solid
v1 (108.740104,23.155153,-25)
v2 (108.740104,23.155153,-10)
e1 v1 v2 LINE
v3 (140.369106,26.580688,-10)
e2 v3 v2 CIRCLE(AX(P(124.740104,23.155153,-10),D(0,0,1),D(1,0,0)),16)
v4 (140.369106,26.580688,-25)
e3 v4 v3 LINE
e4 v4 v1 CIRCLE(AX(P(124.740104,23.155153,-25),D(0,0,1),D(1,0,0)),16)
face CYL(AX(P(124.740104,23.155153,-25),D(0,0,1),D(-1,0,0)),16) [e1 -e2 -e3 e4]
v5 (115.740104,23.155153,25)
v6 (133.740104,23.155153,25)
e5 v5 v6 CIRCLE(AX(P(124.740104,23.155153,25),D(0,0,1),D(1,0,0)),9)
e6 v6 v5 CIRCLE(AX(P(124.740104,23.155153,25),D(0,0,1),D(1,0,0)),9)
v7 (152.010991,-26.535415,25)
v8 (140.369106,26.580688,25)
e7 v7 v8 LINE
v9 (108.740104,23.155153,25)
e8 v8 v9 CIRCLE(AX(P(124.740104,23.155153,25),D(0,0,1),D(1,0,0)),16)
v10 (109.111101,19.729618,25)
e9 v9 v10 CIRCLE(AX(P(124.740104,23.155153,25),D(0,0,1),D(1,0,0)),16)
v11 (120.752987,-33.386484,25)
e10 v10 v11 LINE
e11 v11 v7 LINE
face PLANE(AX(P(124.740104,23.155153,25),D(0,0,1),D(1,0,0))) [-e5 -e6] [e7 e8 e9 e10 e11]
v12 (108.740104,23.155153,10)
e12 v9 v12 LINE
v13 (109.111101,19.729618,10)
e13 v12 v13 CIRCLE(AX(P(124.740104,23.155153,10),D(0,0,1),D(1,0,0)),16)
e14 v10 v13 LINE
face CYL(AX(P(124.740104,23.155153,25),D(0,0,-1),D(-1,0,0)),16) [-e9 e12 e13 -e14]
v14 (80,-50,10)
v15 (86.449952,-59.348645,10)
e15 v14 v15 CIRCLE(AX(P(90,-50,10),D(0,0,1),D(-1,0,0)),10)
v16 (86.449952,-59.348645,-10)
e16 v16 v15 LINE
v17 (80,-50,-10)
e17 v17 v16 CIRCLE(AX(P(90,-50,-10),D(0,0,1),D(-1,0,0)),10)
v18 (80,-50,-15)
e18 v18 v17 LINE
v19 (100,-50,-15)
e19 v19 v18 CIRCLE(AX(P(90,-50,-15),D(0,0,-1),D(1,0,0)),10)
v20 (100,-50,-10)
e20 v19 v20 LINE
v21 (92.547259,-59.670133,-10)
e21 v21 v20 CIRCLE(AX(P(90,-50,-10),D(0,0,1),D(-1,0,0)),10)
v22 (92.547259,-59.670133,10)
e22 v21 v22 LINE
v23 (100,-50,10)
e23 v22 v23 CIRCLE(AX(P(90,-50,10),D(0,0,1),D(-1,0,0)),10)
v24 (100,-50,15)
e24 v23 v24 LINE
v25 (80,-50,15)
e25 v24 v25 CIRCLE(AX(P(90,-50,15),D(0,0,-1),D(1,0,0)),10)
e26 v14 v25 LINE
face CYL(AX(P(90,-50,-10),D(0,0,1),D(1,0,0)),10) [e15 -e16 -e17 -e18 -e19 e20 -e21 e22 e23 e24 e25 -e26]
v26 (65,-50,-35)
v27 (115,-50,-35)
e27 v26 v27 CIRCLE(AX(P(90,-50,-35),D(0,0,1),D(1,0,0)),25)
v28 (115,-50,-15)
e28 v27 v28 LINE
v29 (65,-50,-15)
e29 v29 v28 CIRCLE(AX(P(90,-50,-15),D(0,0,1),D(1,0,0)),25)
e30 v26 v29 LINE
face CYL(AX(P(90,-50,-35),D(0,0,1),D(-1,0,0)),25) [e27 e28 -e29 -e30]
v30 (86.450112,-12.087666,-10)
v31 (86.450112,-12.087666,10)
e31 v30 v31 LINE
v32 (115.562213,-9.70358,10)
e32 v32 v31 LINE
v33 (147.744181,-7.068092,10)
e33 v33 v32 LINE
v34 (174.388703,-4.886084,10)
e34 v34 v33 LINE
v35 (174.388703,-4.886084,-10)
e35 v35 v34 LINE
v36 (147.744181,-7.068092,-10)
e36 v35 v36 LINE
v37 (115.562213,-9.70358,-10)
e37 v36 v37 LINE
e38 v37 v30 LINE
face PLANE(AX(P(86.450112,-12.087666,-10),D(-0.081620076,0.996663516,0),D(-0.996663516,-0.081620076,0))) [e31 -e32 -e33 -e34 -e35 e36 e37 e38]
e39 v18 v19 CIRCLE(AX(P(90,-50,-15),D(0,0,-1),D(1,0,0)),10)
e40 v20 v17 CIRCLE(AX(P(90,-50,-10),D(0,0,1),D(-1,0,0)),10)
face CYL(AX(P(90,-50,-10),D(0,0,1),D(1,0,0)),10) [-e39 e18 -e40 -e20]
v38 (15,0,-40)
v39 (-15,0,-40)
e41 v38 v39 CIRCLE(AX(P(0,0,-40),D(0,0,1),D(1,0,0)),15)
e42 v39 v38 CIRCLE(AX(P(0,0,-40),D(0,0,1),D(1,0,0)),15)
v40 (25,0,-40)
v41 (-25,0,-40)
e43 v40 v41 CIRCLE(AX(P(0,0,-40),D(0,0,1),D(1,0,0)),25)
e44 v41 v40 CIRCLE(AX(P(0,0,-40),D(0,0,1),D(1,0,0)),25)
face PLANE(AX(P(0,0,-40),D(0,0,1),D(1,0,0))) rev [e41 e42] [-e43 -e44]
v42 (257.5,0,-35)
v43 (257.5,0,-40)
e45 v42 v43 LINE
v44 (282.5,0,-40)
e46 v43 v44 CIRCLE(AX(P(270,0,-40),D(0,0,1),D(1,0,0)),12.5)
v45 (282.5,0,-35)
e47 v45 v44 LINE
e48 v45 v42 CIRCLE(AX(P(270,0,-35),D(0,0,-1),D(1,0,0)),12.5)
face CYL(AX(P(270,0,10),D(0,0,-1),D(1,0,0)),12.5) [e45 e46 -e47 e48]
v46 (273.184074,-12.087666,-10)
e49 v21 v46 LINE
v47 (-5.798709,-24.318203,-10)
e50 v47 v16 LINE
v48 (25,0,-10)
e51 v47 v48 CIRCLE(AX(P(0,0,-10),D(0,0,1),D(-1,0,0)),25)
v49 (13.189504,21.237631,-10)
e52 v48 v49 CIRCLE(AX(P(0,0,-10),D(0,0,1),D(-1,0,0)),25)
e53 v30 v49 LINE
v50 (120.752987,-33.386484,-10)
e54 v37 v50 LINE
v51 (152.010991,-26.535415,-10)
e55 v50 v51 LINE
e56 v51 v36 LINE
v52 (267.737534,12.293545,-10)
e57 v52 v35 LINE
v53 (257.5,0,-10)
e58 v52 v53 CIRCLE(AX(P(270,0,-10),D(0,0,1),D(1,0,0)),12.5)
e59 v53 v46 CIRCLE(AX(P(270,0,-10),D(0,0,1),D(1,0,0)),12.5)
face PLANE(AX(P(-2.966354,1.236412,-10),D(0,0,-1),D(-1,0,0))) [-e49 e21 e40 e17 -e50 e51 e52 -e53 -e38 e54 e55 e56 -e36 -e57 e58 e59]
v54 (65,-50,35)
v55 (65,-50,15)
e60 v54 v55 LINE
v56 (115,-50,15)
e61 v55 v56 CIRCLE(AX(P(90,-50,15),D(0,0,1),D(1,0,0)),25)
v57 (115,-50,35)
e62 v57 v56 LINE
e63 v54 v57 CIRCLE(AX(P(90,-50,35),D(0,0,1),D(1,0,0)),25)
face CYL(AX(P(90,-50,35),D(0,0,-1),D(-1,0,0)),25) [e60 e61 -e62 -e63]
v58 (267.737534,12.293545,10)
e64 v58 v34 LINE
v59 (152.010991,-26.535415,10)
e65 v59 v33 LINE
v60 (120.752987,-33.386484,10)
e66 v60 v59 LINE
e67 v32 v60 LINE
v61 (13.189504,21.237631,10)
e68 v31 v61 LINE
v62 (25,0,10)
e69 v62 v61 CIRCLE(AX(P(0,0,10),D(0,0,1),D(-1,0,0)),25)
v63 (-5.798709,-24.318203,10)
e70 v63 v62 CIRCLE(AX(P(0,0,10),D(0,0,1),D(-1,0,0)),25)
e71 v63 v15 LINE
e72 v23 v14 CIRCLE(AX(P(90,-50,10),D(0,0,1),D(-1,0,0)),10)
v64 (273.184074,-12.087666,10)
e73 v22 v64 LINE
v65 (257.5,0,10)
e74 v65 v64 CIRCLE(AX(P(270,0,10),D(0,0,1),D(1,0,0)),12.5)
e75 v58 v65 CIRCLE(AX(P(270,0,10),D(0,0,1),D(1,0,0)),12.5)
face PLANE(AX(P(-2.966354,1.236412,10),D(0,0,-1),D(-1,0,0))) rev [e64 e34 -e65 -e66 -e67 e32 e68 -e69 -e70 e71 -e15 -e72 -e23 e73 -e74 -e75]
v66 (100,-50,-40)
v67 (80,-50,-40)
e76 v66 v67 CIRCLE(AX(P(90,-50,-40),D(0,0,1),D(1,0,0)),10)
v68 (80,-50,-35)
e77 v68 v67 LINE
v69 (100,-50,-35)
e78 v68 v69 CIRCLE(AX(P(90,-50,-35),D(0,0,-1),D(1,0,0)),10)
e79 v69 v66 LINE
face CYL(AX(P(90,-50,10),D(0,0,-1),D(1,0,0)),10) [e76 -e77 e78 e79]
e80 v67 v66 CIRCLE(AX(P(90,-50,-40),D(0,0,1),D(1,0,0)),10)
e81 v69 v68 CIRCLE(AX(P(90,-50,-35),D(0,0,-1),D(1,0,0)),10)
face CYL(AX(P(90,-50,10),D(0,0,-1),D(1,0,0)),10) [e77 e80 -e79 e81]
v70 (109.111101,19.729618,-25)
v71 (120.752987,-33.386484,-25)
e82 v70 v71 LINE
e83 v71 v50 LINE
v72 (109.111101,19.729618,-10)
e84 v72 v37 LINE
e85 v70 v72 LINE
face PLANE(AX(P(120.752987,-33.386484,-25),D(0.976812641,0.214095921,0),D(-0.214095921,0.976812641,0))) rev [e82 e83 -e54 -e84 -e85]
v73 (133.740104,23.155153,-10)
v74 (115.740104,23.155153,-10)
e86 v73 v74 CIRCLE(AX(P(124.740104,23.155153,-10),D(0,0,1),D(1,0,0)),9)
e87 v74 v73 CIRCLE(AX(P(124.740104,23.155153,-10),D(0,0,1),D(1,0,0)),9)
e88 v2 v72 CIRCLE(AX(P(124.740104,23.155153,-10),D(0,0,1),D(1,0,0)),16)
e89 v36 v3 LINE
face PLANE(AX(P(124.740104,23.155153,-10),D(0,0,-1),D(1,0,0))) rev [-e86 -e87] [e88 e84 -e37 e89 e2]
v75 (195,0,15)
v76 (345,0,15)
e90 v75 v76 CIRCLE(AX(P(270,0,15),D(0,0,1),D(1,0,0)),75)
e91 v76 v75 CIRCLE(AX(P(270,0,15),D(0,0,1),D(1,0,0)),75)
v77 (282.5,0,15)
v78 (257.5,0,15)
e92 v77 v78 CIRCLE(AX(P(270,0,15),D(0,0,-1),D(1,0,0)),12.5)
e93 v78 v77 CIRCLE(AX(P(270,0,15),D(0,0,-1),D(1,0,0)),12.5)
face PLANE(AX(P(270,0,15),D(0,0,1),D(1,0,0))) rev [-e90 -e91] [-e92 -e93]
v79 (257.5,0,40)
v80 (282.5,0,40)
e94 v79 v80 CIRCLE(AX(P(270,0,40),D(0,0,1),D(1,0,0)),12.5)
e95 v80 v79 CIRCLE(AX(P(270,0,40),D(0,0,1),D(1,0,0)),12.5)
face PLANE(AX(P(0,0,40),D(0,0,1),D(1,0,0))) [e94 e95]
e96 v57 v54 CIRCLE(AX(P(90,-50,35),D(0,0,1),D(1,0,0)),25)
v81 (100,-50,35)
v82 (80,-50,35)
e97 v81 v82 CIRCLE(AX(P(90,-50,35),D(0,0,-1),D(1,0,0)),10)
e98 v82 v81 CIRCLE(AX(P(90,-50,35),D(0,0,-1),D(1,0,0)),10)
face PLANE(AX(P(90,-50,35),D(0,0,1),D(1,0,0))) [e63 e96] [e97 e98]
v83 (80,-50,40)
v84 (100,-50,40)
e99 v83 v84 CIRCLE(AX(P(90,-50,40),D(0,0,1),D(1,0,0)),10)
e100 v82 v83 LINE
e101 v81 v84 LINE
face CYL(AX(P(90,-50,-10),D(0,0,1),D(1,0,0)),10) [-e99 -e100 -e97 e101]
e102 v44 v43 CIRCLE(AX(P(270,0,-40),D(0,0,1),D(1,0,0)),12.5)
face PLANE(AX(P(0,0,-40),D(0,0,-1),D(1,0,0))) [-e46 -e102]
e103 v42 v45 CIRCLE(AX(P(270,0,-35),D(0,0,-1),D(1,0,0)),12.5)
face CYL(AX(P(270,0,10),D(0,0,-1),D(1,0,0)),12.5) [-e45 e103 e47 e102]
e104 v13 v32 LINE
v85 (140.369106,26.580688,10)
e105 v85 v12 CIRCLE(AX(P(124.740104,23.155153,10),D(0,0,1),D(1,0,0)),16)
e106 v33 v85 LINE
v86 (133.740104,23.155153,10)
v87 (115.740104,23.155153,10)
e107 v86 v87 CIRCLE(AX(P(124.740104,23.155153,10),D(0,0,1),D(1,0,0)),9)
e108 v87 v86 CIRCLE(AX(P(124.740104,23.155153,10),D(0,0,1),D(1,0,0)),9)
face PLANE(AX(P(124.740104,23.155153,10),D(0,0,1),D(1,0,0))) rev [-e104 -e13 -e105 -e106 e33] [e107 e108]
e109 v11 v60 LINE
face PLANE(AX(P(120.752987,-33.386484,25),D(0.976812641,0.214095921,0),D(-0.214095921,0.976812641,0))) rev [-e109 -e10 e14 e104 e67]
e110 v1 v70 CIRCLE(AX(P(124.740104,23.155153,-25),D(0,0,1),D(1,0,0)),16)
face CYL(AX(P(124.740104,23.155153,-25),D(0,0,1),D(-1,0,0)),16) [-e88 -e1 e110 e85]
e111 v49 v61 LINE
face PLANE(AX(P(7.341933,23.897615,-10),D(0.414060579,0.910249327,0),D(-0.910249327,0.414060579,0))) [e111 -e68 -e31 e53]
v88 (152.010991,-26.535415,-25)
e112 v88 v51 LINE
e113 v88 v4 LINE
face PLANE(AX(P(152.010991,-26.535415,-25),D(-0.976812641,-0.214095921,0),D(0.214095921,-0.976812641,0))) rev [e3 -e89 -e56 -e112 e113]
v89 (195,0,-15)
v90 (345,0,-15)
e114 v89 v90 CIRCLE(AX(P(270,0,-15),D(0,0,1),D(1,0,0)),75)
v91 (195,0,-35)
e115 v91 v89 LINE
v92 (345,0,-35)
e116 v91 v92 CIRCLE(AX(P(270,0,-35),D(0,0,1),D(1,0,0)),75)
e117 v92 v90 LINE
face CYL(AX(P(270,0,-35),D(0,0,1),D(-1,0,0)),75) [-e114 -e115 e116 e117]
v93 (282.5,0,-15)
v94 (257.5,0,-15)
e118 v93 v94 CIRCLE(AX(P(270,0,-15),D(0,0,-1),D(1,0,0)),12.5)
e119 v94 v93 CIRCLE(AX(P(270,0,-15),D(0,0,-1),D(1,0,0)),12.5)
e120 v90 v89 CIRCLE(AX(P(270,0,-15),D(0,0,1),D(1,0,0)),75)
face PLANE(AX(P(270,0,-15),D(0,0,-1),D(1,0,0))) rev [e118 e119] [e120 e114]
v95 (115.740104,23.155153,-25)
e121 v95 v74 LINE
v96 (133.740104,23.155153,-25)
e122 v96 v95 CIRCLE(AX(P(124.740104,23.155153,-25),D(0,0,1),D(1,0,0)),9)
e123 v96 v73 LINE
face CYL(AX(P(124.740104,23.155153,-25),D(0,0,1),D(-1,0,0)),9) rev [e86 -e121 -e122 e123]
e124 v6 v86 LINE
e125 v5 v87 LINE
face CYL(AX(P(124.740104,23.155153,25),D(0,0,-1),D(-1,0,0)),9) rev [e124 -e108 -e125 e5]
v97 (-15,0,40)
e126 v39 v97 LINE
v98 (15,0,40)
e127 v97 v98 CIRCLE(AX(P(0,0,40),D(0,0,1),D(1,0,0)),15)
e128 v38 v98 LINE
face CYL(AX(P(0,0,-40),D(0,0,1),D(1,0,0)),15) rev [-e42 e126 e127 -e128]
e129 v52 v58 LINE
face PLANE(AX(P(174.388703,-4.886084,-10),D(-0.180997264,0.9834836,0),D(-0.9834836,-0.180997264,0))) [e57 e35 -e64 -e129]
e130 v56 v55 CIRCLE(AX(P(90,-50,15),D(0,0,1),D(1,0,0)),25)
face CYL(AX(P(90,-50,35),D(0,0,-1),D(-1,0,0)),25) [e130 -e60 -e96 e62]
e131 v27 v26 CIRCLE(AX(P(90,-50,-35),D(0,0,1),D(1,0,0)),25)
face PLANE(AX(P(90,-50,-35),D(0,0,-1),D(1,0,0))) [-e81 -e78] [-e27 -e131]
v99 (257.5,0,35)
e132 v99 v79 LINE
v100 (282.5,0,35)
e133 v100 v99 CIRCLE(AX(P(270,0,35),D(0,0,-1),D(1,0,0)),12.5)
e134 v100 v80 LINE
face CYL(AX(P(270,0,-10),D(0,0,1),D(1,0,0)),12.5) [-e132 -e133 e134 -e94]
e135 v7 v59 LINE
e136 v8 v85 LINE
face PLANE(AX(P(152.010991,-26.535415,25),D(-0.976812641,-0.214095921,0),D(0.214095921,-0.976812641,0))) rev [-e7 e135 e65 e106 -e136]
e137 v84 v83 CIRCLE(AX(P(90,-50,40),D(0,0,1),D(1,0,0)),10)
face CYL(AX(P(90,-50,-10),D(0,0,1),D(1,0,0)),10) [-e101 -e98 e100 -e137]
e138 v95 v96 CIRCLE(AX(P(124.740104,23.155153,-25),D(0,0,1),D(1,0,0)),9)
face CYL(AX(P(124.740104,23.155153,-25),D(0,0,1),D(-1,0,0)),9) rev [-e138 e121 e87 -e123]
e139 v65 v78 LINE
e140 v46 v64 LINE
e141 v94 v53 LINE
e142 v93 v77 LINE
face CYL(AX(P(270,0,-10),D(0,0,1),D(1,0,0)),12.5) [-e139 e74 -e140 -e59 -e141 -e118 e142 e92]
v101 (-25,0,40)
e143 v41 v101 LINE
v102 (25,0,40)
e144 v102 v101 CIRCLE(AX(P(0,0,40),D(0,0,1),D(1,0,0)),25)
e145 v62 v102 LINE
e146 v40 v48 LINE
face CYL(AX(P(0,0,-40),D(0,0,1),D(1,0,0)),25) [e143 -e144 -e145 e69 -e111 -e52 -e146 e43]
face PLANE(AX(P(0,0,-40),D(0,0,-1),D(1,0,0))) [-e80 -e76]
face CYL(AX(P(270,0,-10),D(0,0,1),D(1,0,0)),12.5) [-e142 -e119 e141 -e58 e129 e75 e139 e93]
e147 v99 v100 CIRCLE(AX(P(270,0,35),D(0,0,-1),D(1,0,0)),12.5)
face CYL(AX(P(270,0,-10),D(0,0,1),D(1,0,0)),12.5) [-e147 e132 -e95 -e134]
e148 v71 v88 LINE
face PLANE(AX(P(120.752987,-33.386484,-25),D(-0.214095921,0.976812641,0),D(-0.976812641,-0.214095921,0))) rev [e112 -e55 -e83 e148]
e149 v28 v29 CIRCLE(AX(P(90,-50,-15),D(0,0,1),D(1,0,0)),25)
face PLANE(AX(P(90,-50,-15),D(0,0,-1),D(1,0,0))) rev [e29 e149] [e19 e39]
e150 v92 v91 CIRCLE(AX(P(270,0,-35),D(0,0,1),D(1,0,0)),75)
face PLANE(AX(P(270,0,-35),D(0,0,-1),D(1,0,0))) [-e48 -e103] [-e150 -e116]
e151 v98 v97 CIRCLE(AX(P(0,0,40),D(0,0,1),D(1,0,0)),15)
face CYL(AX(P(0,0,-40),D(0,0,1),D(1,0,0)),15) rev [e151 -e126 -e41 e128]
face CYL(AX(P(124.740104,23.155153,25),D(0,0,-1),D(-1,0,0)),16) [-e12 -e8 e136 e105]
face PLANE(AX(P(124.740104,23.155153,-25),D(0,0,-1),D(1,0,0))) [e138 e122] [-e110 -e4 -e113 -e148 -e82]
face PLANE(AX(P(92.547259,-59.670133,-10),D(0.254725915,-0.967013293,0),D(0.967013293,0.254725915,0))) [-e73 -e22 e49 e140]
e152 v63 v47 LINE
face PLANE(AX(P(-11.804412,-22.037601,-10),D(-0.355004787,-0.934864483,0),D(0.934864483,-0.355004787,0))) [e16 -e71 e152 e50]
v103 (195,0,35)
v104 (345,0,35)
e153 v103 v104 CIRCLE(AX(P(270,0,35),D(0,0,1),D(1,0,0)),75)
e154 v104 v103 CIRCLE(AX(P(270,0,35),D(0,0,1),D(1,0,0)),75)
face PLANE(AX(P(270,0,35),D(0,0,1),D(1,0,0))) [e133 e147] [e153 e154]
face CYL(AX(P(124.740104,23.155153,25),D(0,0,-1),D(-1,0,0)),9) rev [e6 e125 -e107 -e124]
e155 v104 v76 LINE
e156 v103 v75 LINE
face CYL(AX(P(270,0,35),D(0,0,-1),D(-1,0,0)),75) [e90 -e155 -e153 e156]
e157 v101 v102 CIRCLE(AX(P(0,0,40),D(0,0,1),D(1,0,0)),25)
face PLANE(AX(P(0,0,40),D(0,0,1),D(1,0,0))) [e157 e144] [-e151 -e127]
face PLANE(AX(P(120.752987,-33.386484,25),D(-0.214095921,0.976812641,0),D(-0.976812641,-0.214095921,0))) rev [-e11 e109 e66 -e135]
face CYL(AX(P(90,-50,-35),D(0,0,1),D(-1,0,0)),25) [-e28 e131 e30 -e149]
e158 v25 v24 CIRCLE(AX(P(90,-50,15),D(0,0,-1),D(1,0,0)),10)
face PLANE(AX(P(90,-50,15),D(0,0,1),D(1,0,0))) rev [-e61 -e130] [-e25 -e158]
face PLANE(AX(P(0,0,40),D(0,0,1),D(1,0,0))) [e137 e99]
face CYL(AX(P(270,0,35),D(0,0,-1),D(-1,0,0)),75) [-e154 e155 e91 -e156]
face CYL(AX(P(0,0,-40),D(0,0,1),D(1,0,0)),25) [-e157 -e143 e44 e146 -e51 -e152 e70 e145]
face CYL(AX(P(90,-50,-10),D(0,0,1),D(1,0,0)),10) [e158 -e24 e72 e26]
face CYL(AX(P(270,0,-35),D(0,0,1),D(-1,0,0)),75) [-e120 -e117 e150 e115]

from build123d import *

# Parameters (mm, degrees)
EXTRUDE_1_DEPTH      = 40
EXTRUDE_1_DEPTH_BACK = 40
SKETCH_1_R           = 25
SKETCH_1_R_2         = 15
EXTRUDE_2_DEPTH      = 10
EXTRUDE_2_DEPTH_BACK = 10
SKETCH_3_R           = 12.5
SKETCH_3_R_2         = 10
EXTRUDE_3_DEPTH      = 30
SKETCH_4_R           = 25
SKETCH_4_R_2         = 75
BOSS_EXTRUDE4_DEPTH  = 20
SKETCH_5_R           = 9
BOSS_EXTRUDE5_DEPTH  = 15


with BuildPart() as part:
    # 草图1 → 凸台-拉伸1 (new, two sides: drawn at the far end of the back side and taken through both)
    with BuildSketch(Plane.XY.offset(-EXTRUDE_1_DEPTH_BACK)):
        Circle(SKETCH_1_R)
        Circle(SKETCH_1_R_2, mode=Mode.SUBTRACT)
    extrude(amount=EXTRUDE_1_DEPTH + EXTRUDE_1_DEPTH_BACK)

    # 草图2 → 凸台-拉伸2 (add, two sides: drawn at the far end of the back side and taken through both)
    with BuildSketch(Plane.XY.offset(-EXTRUDE_2_DEPTH_BACK)):
        with BuildLine():
            Line((-11.804411719, -22.037601139), (86.449952125, -59.348644826))
            ThreePointArc((86.449952125, -59.348644826), (89.473468939, -59.986128631), (92.547259147, -59.670132928))
            Line((92.547259147, -59.670132928), (273.184073933, -12.08766616))
            ThreePointArc((273.184073933, -12.08766616), (282.19931165, 2.725214721), (267.737534205, 12.293544994))
            Line((267.737534205, 12.293544994), (174.388702716, -4.886083694))
            Line((174.388702716, -4.886083694), (86.450111626, -12.08766616))
            Line((86.450111626, -12.08766616), (7.341932544, 23.897615499))
            ThreePointArc((7.341932544, 23.897615499), (20.013015277, -8.341662634), (-11.804411719, -22.037601139))
        make_face()
    extrude(amount=EXTRUDE_2_DEPTH + EXTRUDE_2_DEPTH_BACK)

    # 草图3 → 凸台-拉伸3 (add)
    with BuildSketch(Plane.XY.offset(10)):
        with Locations((270, 0)):
            Circle(SKETCH_3_R)
        with Locations((90, -50)):
            Circle(SKETCH_3_R_2)
    extrude(amount=EXTRUDE_3_DEPTH)

    # 草图4 → Boss-Extrude4 (add)
    with BuildSketch(Plane.XY.offset(15)):
        with Locations((90, -50)):
            Circle(SKETCH_4_R)
        with Locations((270, 0)):
            Circle(SKETCH_4_R_2)
    extrude(amount=BOSS_EXTRUDE4_DEPTH)

    # 草图5 → Boss-Extrude5 (add)
    with BuildSketch(Plane.XY.offset(10)):
        with BuildLine():
            Line((120.752986945, -33.386484264), (109.111101455, 19.729618285))
            ThreePointArc((109.111101455, 19.729618285), (121.314568975, 38.784155291), (140.36910598, 26.58068777))
            Line((140.36910598, 26.58068777), (152.010991471, -26.535414779))
            Line((152.010991471, -26.535414779), (120.752986945, -33.386484264))
        make_face()
        with Locations((124.740103717, 23.155153028)):
            Circle(SKETCH_5_R, mode=Mode.SUBTRACT)
    extrude(amount=BOSS_EXTRUDE5_DEPTH)

    # Mirror2: part across plane


with BuildPart() as part_1:
    add(part.part)
    add(part.part.mirror(Plane.XY))


solid = part_1.part
